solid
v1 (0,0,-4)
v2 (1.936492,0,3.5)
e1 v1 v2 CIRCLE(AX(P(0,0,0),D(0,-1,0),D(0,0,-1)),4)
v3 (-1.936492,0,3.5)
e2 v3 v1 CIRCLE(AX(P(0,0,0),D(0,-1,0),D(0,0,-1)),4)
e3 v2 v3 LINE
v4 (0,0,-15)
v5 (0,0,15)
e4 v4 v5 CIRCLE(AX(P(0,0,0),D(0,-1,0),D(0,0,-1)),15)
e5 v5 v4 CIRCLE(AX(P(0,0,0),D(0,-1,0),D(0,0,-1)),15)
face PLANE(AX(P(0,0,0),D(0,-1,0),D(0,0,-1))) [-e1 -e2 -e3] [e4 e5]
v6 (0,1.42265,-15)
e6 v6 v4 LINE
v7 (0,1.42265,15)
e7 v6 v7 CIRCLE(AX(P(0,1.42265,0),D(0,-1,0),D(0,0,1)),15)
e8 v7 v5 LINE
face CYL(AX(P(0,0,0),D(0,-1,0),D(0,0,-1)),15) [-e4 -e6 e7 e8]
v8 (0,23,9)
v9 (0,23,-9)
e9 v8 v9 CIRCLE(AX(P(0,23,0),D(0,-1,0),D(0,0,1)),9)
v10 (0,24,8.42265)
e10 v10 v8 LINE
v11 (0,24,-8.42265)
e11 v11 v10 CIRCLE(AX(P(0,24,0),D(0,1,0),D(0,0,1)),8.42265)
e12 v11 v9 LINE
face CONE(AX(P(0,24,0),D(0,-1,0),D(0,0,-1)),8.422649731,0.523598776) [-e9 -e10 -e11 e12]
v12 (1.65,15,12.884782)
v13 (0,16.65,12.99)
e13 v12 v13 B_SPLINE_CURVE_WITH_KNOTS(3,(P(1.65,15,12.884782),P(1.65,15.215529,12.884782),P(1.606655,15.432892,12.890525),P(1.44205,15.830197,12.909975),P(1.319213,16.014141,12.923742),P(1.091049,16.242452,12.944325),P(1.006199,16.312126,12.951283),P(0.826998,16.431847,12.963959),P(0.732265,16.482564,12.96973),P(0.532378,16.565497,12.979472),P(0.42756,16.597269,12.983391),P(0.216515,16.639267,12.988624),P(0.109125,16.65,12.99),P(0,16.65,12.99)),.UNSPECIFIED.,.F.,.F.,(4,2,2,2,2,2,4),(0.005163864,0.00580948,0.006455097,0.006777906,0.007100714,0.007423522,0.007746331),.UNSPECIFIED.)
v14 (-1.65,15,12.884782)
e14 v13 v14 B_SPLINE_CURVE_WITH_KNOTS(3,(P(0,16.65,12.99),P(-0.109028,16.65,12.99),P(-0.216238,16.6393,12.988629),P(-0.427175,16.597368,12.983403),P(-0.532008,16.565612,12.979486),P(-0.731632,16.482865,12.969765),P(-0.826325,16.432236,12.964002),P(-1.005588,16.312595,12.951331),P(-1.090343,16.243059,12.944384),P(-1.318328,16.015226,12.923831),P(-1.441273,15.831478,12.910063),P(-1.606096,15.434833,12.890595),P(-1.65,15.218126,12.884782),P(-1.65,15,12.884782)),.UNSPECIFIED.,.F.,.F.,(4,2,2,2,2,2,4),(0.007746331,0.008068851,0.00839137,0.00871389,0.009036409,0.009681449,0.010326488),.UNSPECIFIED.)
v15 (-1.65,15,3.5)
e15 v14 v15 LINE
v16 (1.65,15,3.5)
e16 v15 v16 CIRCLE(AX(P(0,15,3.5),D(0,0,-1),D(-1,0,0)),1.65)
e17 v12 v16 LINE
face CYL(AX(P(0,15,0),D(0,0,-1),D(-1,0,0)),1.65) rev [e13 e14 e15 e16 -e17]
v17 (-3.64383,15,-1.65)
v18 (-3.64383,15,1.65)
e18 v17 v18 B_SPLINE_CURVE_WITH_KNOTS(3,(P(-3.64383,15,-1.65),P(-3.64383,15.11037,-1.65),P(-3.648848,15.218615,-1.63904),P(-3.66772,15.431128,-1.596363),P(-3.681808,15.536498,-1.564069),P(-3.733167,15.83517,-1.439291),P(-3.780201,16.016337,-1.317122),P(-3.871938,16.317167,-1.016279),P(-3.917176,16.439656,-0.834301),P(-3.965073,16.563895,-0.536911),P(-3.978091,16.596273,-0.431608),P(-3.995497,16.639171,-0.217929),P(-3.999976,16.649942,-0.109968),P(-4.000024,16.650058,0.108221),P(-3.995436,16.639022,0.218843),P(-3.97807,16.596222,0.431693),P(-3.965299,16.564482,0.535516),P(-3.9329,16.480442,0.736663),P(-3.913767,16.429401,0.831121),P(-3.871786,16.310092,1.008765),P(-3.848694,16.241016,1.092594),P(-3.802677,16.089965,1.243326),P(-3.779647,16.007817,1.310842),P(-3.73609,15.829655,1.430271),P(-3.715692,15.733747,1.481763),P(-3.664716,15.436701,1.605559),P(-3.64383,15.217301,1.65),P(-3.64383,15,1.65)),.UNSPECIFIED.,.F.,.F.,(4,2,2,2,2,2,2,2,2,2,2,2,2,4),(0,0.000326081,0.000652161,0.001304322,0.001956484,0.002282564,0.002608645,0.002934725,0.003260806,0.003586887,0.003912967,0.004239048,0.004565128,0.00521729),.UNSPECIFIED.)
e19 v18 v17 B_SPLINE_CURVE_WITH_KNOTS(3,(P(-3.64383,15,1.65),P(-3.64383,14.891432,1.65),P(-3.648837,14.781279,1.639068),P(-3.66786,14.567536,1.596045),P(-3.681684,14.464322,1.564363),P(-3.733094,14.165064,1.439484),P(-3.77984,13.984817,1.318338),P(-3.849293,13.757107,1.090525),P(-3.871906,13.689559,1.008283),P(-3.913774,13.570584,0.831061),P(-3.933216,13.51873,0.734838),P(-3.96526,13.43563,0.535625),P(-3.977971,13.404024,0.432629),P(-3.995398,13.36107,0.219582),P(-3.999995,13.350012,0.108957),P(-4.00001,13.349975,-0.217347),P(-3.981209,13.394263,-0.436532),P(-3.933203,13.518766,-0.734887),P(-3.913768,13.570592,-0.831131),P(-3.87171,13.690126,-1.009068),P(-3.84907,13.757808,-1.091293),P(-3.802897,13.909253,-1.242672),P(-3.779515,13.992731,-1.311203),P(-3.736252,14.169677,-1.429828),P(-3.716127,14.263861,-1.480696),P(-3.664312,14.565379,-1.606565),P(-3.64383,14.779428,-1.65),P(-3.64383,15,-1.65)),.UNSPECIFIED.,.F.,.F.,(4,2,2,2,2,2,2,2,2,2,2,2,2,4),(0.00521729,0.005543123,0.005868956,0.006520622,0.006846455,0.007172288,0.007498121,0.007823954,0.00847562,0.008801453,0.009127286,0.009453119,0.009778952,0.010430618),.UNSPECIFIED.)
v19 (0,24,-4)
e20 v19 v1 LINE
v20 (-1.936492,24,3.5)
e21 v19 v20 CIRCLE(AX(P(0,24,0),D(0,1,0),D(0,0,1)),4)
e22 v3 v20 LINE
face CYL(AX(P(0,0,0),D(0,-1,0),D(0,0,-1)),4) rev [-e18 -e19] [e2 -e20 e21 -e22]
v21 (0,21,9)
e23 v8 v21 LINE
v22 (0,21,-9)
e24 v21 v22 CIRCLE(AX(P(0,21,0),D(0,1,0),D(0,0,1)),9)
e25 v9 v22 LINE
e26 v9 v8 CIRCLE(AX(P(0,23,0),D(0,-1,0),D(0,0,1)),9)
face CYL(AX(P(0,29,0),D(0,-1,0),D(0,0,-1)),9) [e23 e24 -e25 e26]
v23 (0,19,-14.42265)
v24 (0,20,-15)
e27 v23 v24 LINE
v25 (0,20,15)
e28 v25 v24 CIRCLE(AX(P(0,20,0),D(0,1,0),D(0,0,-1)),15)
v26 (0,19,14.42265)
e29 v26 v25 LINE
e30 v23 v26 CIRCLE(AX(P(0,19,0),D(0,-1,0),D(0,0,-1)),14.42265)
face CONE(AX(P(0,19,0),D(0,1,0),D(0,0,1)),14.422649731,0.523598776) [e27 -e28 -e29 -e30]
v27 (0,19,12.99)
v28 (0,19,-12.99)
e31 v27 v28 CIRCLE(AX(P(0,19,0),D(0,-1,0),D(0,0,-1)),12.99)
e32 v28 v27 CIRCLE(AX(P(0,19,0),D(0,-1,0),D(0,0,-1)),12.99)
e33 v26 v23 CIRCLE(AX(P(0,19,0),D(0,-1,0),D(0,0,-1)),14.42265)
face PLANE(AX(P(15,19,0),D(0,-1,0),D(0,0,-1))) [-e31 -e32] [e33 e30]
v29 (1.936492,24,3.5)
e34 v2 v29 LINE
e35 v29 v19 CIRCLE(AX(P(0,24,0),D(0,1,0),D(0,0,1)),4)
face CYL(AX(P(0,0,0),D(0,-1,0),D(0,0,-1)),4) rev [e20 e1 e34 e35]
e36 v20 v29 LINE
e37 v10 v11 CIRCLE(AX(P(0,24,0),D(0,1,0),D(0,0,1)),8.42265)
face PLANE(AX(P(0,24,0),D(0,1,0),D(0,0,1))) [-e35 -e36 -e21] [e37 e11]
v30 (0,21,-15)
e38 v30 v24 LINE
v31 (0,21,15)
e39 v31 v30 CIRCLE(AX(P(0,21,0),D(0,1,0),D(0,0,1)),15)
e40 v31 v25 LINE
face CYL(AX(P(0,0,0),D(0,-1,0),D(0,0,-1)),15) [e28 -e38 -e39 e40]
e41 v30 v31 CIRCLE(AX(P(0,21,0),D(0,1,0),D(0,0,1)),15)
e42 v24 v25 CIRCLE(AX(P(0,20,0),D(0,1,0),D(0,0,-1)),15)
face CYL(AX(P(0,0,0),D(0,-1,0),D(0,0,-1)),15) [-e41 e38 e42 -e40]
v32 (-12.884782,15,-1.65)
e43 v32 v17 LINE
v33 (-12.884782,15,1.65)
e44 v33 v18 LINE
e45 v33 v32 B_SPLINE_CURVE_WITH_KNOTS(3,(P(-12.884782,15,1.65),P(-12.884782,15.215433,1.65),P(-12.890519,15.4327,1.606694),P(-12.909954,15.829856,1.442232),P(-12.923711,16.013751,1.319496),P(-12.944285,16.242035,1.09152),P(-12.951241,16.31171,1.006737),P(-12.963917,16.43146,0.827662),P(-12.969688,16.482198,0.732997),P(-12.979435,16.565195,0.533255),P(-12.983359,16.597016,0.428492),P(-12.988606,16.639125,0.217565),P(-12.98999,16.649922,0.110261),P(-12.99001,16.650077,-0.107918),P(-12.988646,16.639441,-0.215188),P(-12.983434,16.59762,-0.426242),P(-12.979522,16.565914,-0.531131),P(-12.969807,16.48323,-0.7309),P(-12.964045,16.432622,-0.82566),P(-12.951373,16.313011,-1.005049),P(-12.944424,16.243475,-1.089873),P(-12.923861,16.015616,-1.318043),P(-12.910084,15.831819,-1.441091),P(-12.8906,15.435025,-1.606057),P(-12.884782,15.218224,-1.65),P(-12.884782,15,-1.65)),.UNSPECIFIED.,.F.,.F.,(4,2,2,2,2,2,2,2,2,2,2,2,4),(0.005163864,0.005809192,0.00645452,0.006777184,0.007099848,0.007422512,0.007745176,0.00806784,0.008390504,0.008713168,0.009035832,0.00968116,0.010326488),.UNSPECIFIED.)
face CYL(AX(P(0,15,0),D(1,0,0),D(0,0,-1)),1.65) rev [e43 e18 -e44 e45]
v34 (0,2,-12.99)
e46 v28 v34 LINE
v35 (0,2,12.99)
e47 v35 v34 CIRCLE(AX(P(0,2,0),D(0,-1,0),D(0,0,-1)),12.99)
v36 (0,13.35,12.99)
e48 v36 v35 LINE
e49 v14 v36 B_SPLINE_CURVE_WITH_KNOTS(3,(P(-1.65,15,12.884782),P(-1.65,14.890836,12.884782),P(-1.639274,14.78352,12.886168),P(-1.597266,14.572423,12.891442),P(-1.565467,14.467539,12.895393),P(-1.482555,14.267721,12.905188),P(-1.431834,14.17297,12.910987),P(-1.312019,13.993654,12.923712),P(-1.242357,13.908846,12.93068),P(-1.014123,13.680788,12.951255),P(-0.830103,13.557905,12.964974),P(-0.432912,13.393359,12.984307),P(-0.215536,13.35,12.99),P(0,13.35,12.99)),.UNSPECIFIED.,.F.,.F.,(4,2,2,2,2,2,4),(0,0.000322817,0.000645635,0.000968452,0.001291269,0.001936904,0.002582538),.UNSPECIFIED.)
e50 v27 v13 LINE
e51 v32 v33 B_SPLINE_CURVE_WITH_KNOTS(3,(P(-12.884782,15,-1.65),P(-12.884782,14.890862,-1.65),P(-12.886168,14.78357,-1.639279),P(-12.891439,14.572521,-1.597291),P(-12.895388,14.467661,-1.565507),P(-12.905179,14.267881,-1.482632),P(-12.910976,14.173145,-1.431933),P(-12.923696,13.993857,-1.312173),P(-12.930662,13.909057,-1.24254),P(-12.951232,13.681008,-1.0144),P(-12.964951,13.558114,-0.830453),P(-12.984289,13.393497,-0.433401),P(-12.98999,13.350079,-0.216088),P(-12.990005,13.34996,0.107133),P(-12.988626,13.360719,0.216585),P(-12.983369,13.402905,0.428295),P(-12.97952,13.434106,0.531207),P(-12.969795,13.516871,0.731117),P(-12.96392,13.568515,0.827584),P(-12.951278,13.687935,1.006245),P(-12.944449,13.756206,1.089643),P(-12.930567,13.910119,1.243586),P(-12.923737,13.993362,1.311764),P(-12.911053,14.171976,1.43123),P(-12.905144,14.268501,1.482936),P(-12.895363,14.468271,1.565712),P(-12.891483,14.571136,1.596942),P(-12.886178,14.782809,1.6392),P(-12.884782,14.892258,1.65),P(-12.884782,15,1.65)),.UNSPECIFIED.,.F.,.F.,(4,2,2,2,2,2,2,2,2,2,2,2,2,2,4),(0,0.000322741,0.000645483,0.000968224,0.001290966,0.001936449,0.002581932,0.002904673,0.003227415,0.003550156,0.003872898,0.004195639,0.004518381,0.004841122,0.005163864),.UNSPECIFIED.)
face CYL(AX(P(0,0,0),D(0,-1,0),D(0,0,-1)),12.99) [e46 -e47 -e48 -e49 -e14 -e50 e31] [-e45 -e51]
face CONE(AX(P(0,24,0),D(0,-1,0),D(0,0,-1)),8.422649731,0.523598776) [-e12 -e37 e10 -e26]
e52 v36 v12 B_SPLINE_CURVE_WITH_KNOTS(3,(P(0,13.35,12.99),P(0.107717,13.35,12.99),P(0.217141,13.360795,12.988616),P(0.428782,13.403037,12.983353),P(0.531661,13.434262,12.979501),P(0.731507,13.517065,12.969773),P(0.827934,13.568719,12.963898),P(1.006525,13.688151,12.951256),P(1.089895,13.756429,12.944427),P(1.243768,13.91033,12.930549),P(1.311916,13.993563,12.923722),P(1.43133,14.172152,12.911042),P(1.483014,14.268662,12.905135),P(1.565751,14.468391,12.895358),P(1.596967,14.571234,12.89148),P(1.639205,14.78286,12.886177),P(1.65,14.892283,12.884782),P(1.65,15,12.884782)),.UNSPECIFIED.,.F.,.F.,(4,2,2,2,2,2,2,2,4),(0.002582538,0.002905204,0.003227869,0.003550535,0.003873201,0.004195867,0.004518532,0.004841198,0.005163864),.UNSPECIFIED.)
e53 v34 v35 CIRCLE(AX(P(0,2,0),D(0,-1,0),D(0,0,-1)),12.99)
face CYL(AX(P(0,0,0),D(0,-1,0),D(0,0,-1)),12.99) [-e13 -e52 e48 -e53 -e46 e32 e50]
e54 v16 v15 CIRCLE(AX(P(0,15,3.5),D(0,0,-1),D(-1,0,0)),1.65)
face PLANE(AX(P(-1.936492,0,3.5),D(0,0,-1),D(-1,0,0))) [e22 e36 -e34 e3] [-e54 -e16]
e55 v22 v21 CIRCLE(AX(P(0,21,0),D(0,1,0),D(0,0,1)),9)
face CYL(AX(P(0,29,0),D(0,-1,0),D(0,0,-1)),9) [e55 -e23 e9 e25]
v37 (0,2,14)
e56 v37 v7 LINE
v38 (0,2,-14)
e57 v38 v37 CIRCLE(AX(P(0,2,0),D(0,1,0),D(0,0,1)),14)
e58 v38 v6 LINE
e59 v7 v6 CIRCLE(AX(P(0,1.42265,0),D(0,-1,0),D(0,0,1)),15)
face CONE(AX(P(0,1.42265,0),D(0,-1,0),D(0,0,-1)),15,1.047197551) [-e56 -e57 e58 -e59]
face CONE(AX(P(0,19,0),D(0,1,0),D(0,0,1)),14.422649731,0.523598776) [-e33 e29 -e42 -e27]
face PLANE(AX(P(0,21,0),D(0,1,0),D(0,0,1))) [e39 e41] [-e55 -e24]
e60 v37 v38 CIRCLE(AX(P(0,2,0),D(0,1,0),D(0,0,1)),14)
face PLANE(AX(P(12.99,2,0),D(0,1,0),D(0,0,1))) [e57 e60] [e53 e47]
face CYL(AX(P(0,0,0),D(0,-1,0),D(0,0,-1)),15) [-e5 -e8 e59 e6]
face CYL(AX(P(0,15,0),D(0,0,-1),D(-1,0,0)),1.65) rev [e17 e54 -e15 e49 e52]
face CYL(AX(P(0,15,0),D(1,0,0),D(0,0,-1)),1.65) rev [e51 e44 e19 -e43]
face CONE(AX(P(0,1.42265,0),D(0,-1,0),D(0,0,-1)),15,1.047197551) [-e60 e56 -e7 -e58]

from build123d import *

# Parameters (mm, degrees)
SKETCH_5_R               = 20.566311538
CUT_EXTRUDE_1_DEPTH      = 0.5
SKETCH_6_R               = 21.52826295
CUT_EXTRUDE_2_DEPTH      = 0.5
EXTRUDE_START            = 11
SKETCH_7_R               = 8.5
SKETCH_7_R_2             = 4
EXTRUDE_1_DEPTH          = 11
SKETCH_10_R              = 15
CUT_EXTRUDE_3_DEPTH      = 15
SKETCH_11_R              = 15
SKETCH_11_R_2            = 4
EXTRUDE_2_DEPTH          = 0.5
EXTRUDE_START_2          = 0.5
SKETCH_12_R              = 15
SKETCH_12_R_2            = 4
EXTRUDE_3_DEPTH          = 0.5
EXTRUDE_START_3          = 8
SKETCH_14_R              = 7
SKETCH_14_R_2            = 4
EXTRUDE_5_DEPTH          = 8
SKETCH_17_R              = 17.215216586
CUT_EXTRUDE_4_DEPTH      = 30.849623113
SKETCH_18_R              = 9
SKETCH_18_R_2            = 4
EXTRUDE_6_DEPTH          = 8
CHAMFER_1_SIZE           = 1
CHAMFER_1_SIZE2          = 0.577350269
CHAMFER_2_SIZE           = 1
CHAMFER_2_SIZE2          = 0.577350269
CHAMFER_3_SIZE           = 0.5
EXTRUDE_8_DEPTH          = 29
SKETCH_19_W              = 1.65
SKETCH_19_H              = 15
PATTERN_CIRCULAR_1_COUNT = 2
PATTERN_CIRCULAR_1_ANGLE = 90
SKETCH_22_R              = 11.227915354
CUT_EXTRUDE_5_DEPTH      = 5
CHAMFER_4_SIZE           = 1
CHAMFER_4_SIZE2          = 0.577350269


with BuildPart() as part:
    # 草图1 → 旋转1 (revolve)
    with BuildSketch(Plane.XY, mode=Mode.PRIVATE) as revolve_1_sk:
        Polygon((4, 0), (4, 21), (15, 21), (15, 19), (12.99, 19), (12.99, 2), (15, 2), (15, 0), align=None)
    revolve(revolve_1_sk.sketch.rotate(Axis((0, 0, 0), (0, 1, 0)), 90), axis=Axis((0, 0, 0), (0, 1, 0)))

    # 草图5 → 切除-拉伸1 (cut)
    with BuildSketch(Plane.XZ):
        Circle(SKETCH_5_R)
    extrude(amount=-CUT_EXTRUDE_1_DEPTH, mode=Mode.SUBTRACT)

    # 草图6 → 切除-拉伸2 (cut)
    with BuildSketch(Plane(origin=(0, 21, 0), x_dir=(1, 0, 0), z_dir=(0, 1, 0))):
        Circle(SKETCH_6_R)
    extrude(amount=-CUT_EXTRUDE_2_DEPTH, mode=Mode.SUBTRACT)

    # 草图7 → 凸台-拉伸1 (add)
    with BuildSketch(Plane(origin=(0, 20.5, 0), x_dir=(1, 0, 0), z_dir=(0, 1, 0)).offset(EXTRUDE_START)):
        with Locations(Location((0, 0, 0), (0, 0, 270))):
            Circle(SKETCH_7_R)
        with Locations(Location((0, 0, 0), (0, 0, 90))):
            Circle(SKETCH_7_R_2, mode=Mode.SUBTRACT)
    extrude(amount=-EXTRUDE_1_DEPTH)

    # 草图10 → 切除-拉伸3 (cut)
    with BuildSketch(Plane(origin=(0, 20.5, 0), x_dir=(1, 0, 0), z_dir=(0, 1, 0))):
        with Locations(Location((0, 0, 0), (0, 0, 90))):
            Circle(SKETCH_10_R)
    extrude(amount=CUT_EXTRUDE_3_DEPTH, mode=Mode.SUBTRACT)

    # 草图11 → 凸台-拉伸2 (add)
    with BuildSketch(Plane(origin=(0, 20.5, 0), x_dir=(1, 0, 0), z_dir=(0, 1, 0))):
        with Locations(Location((0, 0, 0), (0, 0, 90))):
            Circle(SKETCH_11_R)
        with Locations(Location((0, 0, 0), (0, 0, 90))):
            Circle(SKETCH_11_R_2, mode=Mode.SUBTRACT)
    extrude(amount=EXTRUDE_2_DEPTH)

    # 草图12 → 凸台-拉伸3 (add)
    with BuildSketch(Plane.XZ.offset(-0.5).offset(EXTRUDE_START_2)):
        with Locations(Location((0, 0, 0), (0, 0, 270))):
            Circle(SKETCH_12_R)
        with Locations(Location((0, 0, 0), (0, 0, 270))):
            Circle(SKETCH_12_R_2, mode=Mode.SUBTRACT)
    extrude(amount=-EXTRUDE_3_DEPTH)

    # 草图14 → 凸台-拉伸5 (add)
    with BuildSketch(Plane(origin=(0, 21, 0), x_dir=(1, 0, 0), z_dir=(0, 1, 0)).offset(EXTRUDE_START_3)):
        with Locations(Location((0, 0, 0), (0, 0, 270))):
            Circle(SKETCH_14_R)
        with Locations(Location((0, 0, 0), (0, 0, 90))):
            Circle(SKETCH_14_R_2, mode=Mode.SUBTRACT)
    extrude(amount=-EXTRUDE_5_DEPTH)

    # 草图17 → 切除-拉伸4 (cut, through all)
    with BuildSketch(Plane(origin=(0, 21, 0), x_dir=(1, 0, 0), z_dir=(0, 1, 0))):
        Circle(SKETCH_17_R)
    extrude(amount=CUT_EXTRUDE_4_DEPTH, mode=Mode.SUBTRACT)

    # 草图18 → 凸台-拉伸6 (add)
    with BuildSketch(Plane(origin=(0, 21, 0), x_dir=(1, 0, 0), z_dir=(0, 1, 0)).offset(EXTRUDE_START_3)):
        with Locations(Location((0, 0, 0), (0, 0, 270))):
            Circle(SKETCH_18_R)
        with Locations(Location((0, 0, 0), (0, 0, 90))):
            Circle(SKETCH_18_R_2, mode=Mode.SUBTRACT)
    extrude(amount=-EXTRUDE_6_DEPTH)

    # 倒角1
    chamfer_1_edges = [part.edges().sort_by_distance(p)[0] for p in [
        (0, 19, 15),
    ]]
    chamfer_1_side = [part.faces().sort_by_distance(p)[0] for p in [
        (0, 20, 15),
    ]]
    chamfer(chamfer_1_edges, length=CHAMFER_1_SIZE, length2=CHAMFER_1_SIZE2, reference=chamfer_1_side[0])

    # 倒角2
    chamfer_2_edges = [part.edges().sort_by_distance(p)[0] for p in [
        (0, 2, 15),
    ]]
    chamfer_2_side = [part.faces().sort_by_distance(p)[0] for p in [
        (0, 2, 13.414264069),
    ]]
    chamfer(chamfer_2_edges, length=CHAMFER_2_SIZE, length2=CHAMFER_2_SIZE2, reference=chamfer_2_side[0])

    # 倒角3
    chamfer_3_edges = [part.edges().sort_by_distance(p)[0] for p in [
        (0, 29, -9),
    ]]
    chamfer(chamfer_3_edges, length=CHAMFER_3_SIZE)

    # 草图21 → 凸台-拉伸8 (add, through all)
    with BuildSketch(Plane(origin=(0, 29, 0), x_dir=(1, 0, 0), z_dir=(0, 1, 0))):
        with BuildLine():
            Line((-1.936491673, -3.5), (1.936491673, -3.5))
            ThreePointArc((1.936491673, -3.5), (0, -4), (-1.936491673, -3.5))
        make_face()
    extrude(amount=-EXTRUDE_8_DEPTH)

    # 草图19 → M4 螺纹孔1 (revolve, cut)
    with BuildSketch(Plane(origin=(0, 15, 0), x_dir=(0, 1, 0), z_dir=(1, 0, 0))):
        with Locations((0.825, 7.5)):
            Rectangle(SKETCH_19_W, SKETCH_19_H)
    hole_wizard_m4_1 = revolve(axis=Axis((0, 15, -6.35), (0, 0, 1)), mode=Mode.SUBTRACT)

    # 阵列(圆周)1: M4 螺纹孔1 ×2 about axis
    pattern_circular_1_axis = Axis((0, 0, 0), (0, -1, 0))
    for i in range(1, PATTERN_CIRCULAR_1_COUNT):
        add(hole_wizard_m4_1.rotate(pattern_circular_1_axis, i * PATTERN_CIRCULAR_1_ANGLE / (PATTERN_CIRCULAR_1_COUNT - 1)), mode=Mode.SUBTRACT)

    # 草图22 → 切除-拉伸5 (cut)
    with BuildSketch(Plane(origin=(0, 29, 0), x_dir=(1, 0, 0), z_dir=(0, 1, 0))):
        Circle(SKETCH_22_R)
    extrude(amount=-CUT_EXTRUDE_5_DEPTH, mode=Mode.SUBTRACT)

    # 倒角4
    chamfer_4_edges = [part.edges().sort_by_distance(p)[0] for p in [
        (0, 24, -9),
    ]]
    chamfer_4_side = [part.faces().sort_by_distance(p)[0] for p in [
        (0, 22.5, -9),
    ]]
    chamfer(chamfer_4_edges, length=CHAMFER_4_SIZE, length2=CHAMFER_4_SIZE2, reference=chamfer_4_side[0])


solid = part.part
